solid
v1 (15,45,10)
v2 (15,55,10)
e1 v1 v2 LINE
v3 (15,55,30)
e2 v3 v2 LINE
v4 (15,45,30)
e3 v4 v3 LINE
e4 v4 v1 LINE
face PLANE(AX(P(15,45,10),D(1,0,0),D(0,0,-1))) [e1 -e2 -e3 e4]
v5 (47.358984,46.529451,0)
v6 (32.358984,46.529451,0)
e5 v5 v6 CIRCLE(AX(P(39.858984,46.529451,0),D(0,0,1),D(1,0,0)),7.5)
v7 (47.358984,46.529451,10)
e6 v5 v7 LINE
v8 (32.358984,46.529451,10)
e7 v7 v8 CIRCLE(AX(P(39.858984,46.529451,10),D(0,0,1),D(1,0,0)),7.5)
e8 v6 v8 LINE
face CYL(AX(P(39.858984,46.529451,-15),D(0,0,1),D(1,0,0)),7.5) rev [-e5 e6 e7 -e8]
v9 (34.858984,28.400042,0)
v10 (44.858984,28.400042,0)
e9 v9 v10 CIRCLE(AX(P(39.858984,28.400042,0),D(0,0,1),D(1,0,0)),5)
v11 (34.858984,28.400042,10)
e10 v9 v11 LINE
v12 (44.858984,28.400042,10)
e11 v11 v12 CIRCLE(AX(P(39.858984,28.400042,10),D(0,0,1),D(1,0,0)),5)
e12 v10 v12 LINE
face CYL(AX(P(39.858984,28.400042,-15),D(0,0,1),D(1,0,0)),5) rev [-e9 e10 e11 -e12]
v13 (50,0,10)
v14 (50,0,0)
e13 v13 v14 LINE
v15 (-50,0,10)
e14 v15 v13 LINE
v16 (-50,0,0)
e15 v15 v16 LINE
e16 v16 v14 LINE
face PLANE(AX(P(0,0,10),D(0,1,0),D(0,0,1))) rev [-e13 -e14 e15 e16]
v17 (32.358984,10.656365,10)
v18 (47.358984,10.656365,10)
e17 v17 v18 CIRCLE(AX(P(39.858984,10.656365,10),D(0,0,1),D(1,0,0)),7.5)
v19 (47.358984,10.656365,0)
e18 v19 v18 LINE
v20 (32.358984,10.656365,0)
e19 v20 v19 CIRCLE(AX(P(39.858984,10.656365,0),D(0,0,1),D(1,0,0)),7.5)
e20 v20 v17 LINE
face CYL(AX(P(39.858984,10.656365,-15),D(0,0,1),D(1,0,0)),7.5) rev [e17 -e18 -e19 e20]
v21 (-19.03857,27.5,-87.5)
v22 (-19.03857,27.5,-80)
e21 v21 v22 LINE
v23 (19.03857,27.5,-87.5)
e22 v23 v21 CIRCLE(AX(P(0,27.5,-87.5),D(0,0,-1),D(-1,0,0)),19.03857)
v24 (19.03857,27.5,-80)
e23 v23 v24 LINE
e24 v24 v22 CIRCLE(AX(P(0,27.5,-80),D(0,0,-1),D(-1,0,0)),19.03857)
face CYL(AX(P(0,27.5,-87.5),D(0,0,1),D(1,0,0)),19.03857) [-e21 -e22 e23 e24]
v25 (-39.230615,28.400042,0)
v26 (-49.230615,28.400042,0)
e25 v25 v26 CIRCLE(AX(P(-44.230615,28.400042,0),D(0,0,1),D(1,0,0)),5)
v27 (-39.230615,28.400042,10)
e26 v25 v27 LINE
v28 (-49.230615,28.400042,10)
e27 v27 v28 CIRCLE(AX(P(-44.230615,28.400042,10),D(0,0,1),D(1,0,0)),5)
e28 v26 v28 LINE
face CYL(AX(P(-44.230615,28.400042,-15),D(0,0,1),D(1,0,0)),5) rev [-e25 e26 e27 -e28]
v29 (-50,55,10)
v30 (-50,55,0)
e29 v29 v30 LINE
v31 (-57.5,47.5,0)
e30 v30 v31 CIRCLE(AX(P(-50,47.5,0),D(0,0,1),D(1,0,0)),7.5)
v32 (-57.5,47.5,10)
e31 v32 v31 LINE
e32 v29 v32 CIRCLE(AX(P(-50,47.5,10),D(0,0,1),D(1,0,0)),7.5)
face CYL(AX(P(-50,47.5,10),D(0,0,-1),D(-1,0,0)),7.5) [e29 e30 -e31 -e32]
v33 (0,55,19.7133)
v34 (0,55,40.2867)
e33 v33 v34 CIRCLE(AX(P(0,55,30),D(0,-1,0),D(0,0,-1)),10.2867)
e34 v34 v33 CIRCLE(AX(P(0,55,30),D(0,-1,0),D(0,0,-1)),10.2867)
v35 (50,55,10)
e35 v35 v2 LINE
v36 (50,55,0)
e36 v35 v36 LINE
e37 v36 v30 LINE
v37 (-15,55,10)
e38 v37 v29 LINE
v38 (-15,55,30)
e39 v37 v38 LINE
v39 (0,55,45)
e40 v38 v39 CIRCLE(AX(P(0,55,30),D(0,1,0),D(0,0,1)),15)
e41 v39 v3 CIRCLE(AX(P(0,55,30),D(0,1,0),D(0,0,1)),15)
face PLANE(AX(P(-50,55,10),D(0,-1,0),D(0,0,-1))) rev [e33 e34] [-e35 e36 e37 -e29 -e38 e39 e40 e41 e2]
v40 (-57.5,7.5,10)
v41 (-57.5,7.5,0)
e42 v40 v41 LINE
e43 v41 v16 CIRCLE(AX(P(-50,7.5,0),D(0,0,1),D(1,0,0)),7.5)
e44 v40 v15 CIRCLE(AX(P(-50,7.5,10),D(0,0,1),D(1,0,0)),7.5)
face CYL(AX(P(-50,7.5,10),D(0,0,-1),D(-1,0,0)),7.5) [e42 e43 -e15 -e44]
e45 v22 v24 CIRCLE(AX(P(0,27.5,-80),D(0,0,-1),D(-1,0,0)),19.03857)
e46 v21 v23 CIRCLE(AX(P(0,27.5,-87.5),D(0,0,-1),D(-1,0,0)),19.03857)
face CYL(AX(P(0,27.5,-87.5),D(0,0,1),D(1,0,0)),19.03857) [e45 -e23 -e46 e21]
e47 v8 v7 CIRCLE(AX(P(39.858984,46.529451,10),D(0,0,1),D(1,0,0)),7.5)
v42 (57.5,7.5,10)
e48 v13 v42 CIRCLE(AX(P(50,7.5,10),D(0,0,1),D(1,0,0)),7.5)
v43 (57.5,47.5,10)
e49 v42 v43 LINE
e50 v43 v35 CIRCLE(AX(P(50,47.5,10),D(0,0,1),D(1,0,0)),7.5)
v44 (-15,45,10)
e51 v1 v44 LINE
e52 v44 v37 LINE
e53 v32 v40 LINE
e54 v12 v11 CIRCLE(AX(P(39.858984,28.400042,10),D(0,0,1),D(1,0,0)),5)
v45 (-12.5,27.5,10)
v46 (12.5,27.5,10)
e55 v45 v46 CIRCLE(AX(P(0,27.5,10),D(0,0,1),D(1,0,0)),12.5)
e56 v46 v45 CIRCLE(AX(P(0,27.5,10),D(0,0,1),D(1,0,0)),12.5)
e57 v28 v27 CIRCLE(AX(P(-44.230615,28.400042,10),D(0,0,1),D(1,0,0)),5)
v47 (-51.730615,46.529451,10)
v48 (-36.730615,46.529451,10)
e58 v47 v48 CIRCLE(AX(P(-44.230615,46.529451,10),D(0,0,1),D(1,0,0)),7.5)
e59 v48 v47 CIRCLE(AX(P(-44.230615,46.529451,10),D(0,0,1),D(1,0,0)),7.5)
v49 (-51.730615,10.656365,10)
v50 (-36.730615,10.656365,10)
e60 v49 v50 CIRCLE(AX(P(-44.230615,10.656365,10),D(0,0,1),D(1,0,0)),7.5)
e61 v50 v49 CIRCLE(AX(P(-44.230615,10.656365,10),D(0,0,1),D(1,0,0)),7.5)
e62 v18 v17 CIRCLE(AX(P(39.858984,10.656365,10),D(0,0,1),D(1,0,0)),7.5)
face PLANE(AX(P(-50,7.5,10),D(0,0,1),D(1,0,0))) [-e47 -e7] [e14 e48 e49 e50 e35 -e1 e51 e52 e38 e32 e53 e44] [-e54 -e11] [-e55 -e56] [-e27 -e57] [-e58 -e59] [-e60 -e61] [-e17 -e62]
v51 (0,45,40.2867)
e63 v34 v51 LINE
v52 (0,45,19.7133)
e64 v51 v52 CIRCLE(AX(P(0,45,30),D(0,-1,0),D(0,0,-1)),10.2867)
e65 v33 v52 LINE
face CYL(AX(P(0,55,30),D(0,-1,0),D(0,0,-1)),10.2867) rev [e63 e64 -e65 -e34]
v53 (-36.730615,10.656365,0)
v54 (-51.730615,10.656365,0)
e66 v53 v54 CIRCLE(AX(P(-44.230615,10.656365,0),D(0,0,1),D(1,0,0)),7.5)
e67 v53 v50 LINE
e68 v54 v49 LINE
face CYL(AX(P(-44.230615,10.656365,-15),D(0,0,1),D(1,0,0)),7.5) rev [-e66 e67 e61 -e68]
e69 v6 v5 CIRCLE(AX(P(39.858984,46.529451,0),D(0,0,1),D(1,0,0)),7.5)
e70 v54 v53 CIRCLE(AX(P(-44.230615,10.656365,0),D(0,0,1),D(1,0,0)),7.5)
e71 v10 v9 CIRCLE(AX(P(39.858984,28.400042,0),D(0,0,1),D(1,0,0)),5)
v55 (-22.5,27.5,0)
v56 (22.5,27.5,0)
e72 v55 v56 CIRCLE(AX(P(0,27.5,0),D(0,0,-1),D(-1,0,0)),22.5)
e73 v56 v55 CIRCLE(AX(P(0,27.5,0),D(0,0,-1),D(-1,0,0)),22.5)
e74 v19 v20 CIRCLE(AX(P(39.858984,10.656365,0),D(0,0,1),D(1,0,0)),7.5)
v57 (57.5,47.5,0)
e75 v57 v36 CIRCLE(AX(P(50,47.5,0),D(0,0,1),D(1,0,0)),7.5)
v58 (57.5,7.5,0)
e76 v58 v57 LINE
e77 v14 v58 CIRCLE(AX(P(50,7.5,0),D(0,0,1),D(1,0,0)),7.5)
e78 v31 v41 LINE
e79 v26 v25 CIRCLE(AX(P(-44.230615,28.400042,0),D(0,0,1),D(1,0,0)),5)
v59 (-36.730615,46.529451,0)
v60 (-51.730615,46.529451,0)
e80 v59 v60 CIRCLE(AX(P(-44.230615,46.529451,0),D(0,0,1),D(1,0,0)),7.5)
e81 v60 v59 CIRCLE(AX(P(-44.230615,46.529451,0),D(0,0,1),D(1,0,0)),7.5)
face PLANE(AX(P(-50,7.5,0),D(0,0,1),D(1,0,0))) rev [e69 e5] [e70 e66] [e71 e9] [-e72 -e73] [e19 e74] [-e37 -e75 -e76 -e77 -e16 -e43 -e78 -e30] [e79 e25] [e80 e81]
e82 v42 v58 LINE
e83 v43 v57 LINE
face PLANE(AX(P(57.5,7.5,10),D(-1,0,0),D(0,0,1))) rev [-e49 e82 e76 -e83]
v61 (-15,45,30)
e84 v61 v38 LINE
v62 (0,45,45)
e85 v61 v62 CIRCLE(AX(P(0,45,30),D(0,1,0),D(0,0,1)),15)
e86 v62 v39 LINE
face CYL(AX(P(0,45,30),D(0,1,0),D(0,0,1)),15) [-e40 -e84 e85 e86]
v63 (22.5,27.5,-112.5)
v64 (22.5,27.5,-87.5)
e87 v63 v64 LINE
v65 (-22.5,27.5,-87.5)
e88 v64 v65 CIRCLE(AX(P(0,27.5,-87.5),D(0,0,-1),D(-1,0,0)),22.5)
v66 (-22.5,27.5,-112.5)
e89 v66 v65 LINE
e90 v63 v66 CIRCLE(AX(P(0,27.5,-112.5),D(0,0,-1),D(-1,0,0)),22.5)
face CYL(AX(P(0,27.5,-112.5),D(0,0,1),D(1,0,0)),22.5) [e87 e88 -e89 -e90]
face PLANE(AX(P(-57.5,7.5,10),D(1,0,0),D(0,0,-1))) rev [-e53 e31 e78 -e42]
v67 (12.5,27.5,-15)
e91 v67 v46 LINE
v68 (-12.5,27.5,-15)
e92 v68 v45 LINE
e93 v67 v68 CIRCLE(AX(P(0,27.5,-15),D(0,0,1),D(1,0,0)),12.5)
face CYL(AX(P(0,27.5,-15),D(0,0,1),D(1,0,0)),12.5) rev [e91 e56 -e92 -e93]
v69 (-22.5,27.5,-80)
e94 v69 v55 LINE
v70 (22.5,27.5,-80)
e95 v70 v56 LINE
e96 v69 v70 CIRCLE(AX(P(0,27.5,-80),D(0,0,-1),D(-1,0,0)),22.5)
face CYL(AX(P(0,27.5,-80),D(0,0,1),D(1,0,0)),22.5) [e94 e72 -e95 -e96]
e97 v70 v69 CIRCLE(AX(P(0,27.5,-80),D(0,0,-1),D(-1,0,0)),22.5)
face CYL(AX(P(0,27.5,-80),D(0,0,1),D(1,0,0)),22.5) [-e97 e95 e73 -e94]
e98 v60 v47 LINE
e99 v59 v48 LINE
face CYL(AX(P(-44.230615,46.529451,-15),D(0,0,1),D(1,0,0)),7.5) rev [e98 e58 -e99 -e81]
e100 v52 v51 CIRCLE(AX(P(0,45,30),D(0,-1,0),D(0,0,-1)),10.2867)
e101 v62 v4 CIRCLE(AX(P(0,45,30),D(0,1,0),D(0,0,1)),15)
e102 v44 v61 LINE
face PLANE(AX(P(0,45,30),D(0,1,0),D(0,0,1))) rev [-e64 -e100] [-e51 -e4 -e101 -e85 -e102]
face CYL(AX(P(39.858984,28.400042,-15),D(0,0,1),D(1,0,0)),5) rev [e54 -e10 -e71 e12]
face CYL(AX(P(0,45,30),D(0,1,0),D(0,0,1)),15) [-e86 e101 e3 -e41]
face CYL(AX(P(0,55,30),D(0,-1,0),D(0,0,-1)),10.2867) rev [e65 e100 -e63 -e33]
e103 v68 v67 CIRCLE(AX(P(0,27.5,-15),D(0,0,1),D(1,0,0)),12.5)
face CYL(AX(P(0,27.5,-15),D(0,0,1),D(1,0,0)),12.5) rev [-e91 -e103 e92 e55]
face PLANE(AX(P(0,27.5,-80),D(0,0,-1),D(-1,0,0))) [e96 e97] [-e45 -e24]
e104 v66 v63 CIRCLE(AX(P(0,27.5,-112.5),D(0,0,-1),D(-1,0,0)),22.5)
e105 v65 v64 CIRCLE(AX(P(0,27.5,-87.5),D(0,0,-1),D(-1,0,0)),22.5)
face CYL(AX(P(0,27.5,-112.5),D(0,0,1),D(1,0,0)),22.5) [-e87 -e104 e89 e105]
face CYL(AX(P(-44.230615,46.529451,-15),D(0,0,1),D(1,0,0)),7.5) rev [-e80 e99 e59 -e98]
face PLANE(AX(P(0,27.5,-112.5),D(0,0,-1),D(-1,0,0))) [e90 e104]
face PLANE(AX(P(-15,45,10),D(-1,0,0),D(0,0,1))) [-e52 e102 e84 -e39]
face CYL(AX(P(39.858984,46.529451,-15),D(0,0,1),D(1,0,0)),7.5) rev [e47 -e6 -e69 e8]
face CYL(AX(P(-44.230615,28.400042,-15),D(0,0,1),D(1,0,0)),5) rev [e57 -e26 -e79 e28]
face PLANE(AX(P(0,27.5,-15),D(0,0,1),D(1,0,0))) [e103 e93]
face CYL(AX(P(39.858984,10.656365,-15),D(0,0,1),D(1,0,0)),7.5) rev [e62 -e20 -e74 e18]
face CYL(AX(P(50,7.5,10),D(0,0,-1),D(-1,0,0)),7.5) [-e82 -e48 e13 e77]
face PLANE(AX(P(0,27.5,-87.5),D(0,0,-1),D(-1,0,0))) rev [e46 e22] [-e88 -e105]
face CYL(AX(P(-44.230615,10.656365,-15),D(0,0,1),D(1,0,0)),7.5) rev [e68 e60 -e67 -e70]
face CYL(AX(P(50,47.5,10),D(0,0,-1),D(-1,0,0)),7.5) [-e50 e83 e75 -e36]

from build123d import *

# Parameters (mm, degrees)
FLANGE_PLATE_DEPTH      = 10
SHAFT_45_SKETCH_R       = 22.5
SHAFT_45_DEPTH          = 80
GROOVE_NECK_SKETCH_R    = 19.038570364
GROOVE_NECK_38_DEPTH    = 7.5
SHAFT_END_SKETCH_R      = 22.5
SHAFT_END_45_DEPTH      = 25
CENTRE_BORE_SKETCH_R    = 12.5
CENTRE_BORE_25_DEPTH    = 25
FLANGE_HOLES_SKETCH_R   = 7.5
FLANGE_HOLES_SKETCH_R_2 = 5
FLANGE_HOLES_6X_DEPTH   = 25
LUG_DEPTH               = 10
LUG_HOLE_SKETCH_R       = 10.286699657
LUG_HOLE_20_6_DEPTH     = 10


with BuildPart() as part:
    # Flange Plate Sketch → Flange Plate (new body)
    with BuildSketch(Plane.XY):
        with BuildLine():
            Line((0, 0), (50, 0))
            ThreePointArc((50, 0), (55.303300859, 2.196699141), (57.5, 7.5))
            Line((57.5, 7.5), (57.5, 47.5))
            ThreePointArc((57.5, 47.5), (55.303300859, 52.803300859), (50, 55))
            Line((50, 55), (-50, 55))
            ThreePointArc((-50, 55), (-55.303300859, 52.803300859), (-57.5, 47.5))
            Line((-57.5, 47.5), (-57.5, 7.5))
            ThreePointArc((-57.5, 7.5), (-55.303300859, 2.196699141), (-50, 0))
            Line((-50, 0), (0, 0))
        make_face()
    extrude(amount=FLANGE_PLATE_DEPTH)

    # Shaft Ø45 Sketch → Shaft Ø45 (add)
    with BuildSketch(Plane(origin=(0, 0, 0), x_dir=(-1, 0, 0), z_dir=(0, 0, -1))):
        with Locations((0, 27.5)):
            Circle(SHAFT_45_SKETCH_R)
    extrude(amount=SHAFT_45_DEPTH)

    # Groove Neck Sketch → Groove Neck Ø38 (add)
    with BuildSketch(Plane(origin=(0, 0, -80), x_dir=(-1, 0, 0), z_dir=(0, 0, -1))):
        with Locations((0, 27.5)):
            Circle(GROOVE_NECK_SKETCH_R)
    extrude(amount=GROOVE_NECK_38_DEPTH)

    # Shaft End Sketch → Shaft End Ø45 (add)
    with BuildSketch(Plane(origin=(0, 0, -87.5), x_dir=(-1, 0, 0), z_dir=(0, 0, -1))):
        with Locations((0, 27.5)):
            Circle(SHAFT_END_SKETCH_R)
    extrude(amount=SHAFT_END_45_DEPTH)

    # Centre Bore Sketch → Centre Bore Ø25 (cut)
    with BuildSketch(Plane.XY.offset(10)):
        with Locations((0, 27.5)):
            Circle(CENTRE_BORE_SKETCH_R)
    extrude(amount=-CENTRE_BORE_25_DEPTH, mode=Mode.SUBTRACT)

    # Flange Holes Sketch → Flange Holes 6x (cut)
    with BuildSketch(Plane.XY.offset(10)):
        with Locations((39.858984169, 46.529450506)):
            Circle(FLANGE_HOLES_SKETCH_R)
        with Locations((39.858984169, 28.400041578)):
            Circle(FLANGE_HOLES_SKETCH_R_2)
        with Locations((39.858984169, 10.656364754)):
            Circle(FLANGE_HOLES_SKETCH_R)
        with Locations((-44.230614691, 10.656364754)):
            Circle(FLANGE_HOLES_SKETCH_R)
        with Locations((-44.230614691, 28.400041578)):
            Circle(FLANGE_HOLES_SKETCH_R_2)
        with Locations((-44.230614691, 46.529450506)):
            Circle(FLANGE_HOLES_SKETCH_R)
    extrude(amount=-FLANGE_HOLES_6X_DEPTH, mode=Mode.SUBTRACT)

    # Lug Sketch → Lug (add)
    with BuildSketch(Plane(origin=(0, 55, 0), x_dir=(1, 0, 0), z_dir=(0, 1, 0))):
        with BuildLine():
            Line((0, -10), (-15, -10))
            Line((-15, -10), (-15, -30))
            ThreePointArc((-15, -30), (0, -45), (15, -30))
            Line((15, -30), (15, -10))
            Line((15, -10), (0, -10))
        make_face()
    extrude(amount=-LUG_DEPTH)

    # Lug Hole Sketch → Lug Hole Ø20.6 (cut)
    with BuildSketch(Plane.XZ.offset(-45)):
        with Locations(Location((0, 30, 0), (0, 0, 270))):
            Circle(LUG_HOLE_SKETCH_R)
    extrude(amount=-LUG_HOLE_20_6_DEPTH, mode=Mode.SUBTRACT)


solid = part.part
